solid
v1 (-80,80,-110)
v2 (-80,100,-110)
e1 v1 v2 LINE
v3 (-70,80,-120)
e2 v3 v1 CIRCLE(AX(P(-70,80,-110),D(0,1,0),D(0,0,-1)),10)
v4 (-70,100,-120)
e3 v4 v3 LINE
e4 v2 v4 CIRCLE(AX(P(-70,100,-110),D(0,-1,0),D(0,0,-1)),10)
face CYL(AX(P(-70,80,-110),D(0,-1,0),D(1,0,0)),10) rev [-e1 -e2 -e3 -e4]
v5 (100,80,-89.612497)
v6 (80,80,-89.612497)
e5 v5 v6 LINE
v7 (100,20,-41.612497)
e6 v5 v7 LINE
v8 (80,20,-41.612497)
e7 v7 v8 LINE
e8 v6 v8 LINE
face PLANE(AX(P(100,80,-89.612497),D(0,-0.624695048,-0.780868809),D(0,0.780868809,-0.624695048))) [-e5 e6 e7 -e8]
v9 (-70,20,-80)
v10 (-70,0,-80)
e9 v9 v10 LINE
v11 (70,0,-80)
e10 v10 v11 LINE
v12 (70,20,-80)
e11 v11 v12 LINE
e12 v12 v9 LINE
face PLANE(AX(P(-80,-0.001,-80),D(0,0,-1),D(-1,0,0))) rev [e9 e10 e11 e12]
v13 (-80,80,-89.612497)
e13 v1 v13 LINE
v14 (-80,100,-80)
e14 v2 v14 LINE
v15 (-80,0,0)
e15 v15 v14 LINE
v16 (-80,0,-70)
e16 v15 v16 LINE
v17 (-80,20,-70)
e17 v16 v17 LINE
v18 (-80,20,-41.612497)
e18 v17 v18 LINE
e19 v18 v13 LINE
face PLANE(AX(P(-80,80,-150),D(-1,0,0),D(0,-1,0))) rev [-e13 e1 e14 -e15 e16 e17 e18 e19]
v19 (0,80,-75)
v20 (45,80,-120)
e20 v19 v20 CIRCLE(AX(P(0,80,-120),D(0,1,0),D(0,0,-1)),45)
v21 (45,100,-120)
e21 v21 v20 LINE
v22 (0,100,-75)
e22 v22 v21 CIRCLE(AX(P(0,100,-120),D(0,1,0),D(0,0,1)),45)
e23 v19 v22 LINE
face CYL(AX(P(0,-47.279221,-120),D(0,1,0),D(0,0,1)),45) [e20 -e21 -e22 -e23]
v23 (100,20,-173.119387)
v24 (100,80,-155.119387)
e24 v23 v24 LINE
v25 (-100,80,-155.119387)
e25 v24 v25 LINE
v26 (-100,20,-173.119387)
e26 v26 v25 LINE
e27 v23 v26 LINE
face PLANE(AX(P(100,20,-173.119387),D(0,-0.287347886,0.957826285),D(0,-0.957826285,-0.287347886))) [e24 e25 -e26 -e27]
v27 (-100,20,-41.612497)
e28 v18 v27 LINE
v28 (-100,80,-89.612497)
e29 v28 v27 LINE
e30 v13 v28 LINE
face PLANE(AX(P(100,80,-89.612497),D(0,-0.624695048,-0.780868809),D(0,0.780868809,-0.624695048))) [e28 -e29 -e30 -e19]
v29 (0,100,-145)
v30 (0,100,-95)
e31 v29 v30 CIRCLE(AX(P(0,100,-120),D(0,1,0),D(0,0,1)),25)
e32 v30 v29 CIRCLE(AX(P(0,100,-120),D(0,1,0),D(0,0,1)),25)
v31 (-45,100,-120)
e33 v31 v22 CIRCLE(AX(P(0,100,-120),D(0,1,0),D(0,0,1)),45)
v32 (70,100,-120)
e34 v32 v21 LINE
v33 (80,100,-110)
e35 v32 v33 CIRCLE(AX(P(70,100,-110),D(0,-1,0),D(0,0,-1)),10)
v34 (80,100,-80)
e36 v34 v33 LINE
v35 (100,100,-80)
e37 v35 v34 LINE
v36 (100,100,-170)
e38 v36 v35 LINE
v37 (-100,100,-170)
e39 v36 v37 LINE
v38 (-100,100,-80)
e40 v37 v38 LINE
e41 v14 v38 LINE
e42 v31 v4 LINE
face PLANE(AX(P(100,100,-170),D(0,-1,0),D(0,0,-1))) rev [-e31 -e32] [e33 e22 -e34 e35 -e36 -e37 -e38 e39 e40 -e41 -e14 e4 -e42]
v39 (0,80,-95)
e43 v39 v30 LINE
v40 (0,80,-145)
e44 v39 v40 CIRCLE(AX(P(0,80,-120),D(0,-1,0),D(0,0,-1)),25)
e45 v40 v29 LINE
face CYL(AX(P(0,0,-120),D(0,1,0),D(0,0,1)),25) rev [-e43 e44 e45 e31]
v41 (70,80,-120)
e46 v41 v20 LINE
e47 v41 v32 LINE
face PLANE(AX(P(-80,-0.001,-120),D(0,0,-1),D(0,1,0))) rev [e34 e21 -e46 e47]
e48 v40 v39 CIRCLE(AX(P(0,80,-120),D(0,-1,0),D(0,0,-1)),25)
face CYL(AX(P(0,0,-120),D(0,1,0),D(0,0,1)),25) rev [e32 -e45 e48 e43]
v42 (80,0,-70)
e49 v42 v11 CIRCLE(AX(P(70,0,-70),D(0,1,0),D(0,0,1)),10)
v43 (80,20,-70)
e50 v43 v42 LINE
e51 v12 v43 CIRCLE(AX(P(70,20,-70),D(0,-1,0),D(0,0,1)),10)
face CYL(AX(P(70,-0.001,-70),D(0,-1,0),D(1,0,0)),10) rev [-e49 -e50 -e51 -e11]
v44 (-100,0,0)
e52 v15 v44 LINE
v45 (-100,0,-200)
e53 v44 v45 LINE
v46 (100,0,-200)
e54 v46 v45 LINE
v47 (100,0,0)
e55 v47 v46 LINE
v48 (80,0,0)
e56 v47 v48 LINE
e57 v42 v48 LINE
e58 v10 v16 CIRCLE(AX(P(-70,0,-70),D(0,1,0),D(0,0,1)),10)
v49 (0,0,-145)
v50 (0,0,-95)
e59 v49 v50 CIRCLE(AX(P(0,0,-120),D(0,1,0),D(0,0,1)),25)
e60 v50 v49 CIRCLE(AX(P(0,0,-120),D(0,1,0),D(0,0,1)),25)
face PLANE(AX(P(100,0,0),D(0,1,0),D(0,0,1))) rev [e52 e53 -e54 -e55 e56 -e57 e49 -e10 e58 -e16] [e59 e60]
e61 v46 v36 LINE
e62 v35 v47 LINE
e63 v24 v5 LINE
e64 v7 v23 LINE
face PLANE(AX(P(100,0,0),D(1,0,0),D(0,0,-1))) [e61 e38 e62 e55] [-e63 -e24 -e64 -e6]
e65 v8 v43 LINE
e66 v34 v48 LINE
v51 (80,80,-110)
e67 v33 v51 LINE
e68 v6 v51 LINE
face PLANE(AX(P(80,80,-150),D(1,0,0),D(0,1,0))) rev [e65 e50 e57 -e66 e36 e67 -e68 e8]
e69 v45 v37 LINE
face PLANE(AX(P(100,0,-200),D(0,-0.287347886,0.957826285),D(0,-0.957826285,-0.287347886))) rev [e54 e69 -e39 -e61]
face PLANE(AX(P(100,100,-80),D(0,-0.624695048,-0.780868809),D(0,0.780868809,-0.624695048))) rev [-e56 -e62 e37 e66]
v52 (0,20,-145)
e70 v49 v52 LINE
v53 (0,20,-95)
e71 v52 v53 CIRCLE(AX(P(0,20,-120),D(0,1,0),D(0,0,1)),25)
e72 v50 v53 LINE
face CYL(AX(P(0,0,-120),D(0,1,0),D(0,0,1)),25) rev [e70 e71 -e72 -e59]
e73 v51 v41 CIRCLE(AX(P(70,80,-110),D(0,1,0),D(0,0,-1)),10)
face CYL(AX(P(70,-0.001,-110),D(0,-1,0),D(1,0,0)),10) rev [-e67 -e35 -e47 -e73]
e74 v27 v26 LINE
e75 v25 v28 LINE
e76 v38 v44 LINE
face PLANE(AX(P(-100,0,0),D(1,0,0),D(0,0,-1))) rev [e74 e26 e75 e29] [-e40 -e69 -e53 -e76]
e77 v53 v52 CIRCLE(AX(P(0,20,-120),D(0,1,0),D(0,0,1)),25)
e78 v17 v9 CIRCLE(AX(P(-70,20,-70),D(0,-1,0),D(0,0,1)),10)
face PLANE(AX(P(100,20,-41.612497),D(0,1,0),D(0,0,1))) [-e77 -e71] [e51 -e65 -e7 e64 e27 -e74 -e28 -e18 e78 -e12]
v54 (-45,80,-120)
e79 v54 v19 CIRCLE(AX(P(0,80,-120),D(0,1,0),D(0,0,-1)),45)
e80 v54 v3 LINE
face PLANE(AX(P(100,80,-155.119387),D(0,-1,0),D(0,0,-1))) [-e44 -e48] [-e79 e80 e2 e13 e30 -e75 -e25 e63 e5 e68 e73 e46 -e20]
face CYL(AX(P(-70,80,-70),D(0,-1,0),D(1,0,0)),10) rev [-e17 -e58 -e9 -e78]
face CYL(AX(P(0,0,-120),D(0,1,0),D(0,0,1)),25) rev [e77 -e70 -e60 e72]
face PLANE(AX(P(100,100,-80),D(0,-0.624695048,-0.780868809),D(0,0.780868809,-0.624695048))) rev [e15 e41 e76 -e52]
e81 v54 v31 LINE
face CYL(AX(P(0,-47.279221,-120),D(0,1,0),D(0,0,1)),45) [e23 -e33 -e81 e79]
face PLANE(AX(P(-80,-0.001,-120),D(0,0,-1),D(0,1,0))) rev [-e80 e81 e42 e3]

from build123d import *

# Parameters (mm, degrees)
FRAME_BODY_200_DEPTH        = 100
CENTRE_RECESS_SKETCH_W      = 160
CENTRE_RECESS_SKETCH_H      = 60
CENTRE_RECESS_CUT_DEPTH     = 150
WINDOW_A_CUT_REACH          = 246.949
WINDOW_A_SKETCH_80X60_W     = 160
WINDOW_A_SKETCH_80X60_H     = 60
WINDOW_B_CUT_REACH          = 239.487
WINDOW_B_SKETCH_W           = 160
WINDOW_B_SKETCH_H           = 80
WINDOW_CORNER_FILLETS_R10_R = 10
ANCHOR_BOSS_SKETCH_90_R     = 45
ANCHOR_BOSS_90_DEPTH        = 20
ANCHOR_BORE_SKETCH_50_R     = 25
ANCHOR_BORE_50_DEPTH        = 245.948974278


with BuildPart() as part:
    # Frame Profile Sketch → Frame Body 200 (new, symmetric)
    with BuildSketch(Plane(origin=(0, 0, 0), x_dir=(0, 0, -1), z_dir=(1, 0, 0))):
        Polygon((200, 0), (170, 100), (80, 100), (0, 0), align=None)
        Polygon((155.119386982, 80), (89.61249695, 80), (41.61249695, 20), (173.119386982, 20), align=None, mode=Mode.SUBTRACT)
    extrude(amount=FRAME_BODY_200_DEPTH, both=True)

    # Centre Recess Sketch → Centre Recess Cut (cut)
    with BuildSketch(Plane.XY):
        with Locations((0, 50)):
            Rectangle(CENTRE_RECESS_SKETCH_W, CENTRE_RECESS_SKETCH_H)
    extrude(amount=-CENTRE_RECESS_CUT_DEPTH, mode=Mode.SUBTRACT)

    # Window A Sketch 80x60 → Window A Cut (cut, up to next)
    with BuildSketch(Plane(origin=(0, 100, 0), x_dir=(1, 0, 0), z_dir=(0, 1, 0)), mode=Mode.PRIVATE) as window_a_cut_sk1:
        with Locations((0, 90)):
            Rectangle(WINDOW_A_SKETCH_80X60_W, WINDOW_A_SKETCH_80X60_H)
    window_a_cut_tool1 = extrude(window_a_cut_sk1.sketch, amount=-WINDOW_A_CUT_REACH, mode=Mode.PRIVATE) & part.part
    add(window_a_cut_tool1.solids().sort_by_distance((0, 100, -90))[0], mode=Mode.SUBTRACT)

    # Window B Sketch → Window B Cut (cut, up to next)
    with BuildSketch(Plane(origin=(0, 20, 0), x_dir=(1, 0, 0), z_dir=(0, 1, 0)), mode=Mode.PRIVATE) as window_b_cut_sk1:
        with Locations((0, 40)):
            Rectangle(WINDOW_B_SKETCH_W, WINDOW_B_SKETCH_H)
    window_b_cut_tool1 = extrude(window_b_cut_sk1.sketch, amount=-WINDOW_B_CUT_REACH, mode=Mode.PRIVATE) & part.part
    add(window_b_cut_tool1.solids().sort_by_distance((0, 20, -40))[0], mode=Mode.SUBTRACT)

    # Window Corner Fillets R10
    window_corner_fillets_r10_edges = [part.edges().sort_by_distance(p)[0] for p in [
        (80, 90, -120),
        (-80, 90, -120),
        (-80, 10, -80),
        (80, 10, -80),
    ]]
    fillet(window_corner_fillets_r10_edges, radius=WINDOW_CORNER_FILLETS_R10_R)

    # Anchor Boss Sketch Ø90 → Anchor Boss Ø90 (add)
    with BuildSketch(Plane(origin=(0, 100, 0), x_dir=(1, 0, 0), z_dir=(0, 1, 0))):
        with Locations((0, 120)):
            Circle(ANCHOR_BOSS_SKETCH_90_R)
    extrude(amount=-ANCHOR_BOSS_90_DEPTH)

    # Anchor Bore Sketch Ø50 → Anchor Bore Ø50 (cut, through all)
    with BuildSketch(Plane(origin=(0, 100, 0), x_dir=(1, 0, 0), z_dir=(0, 1, 0))):
        with Locations(Location((0, 120, 0), (0, 0, 270))):
            Circle(ANCHOR_BORE_SKETCH_50_R)
    extrude(amount=-ANCHOR_BORE_50_DEPTH, mode=Mode.SUBTRACT)


solid = part.part
